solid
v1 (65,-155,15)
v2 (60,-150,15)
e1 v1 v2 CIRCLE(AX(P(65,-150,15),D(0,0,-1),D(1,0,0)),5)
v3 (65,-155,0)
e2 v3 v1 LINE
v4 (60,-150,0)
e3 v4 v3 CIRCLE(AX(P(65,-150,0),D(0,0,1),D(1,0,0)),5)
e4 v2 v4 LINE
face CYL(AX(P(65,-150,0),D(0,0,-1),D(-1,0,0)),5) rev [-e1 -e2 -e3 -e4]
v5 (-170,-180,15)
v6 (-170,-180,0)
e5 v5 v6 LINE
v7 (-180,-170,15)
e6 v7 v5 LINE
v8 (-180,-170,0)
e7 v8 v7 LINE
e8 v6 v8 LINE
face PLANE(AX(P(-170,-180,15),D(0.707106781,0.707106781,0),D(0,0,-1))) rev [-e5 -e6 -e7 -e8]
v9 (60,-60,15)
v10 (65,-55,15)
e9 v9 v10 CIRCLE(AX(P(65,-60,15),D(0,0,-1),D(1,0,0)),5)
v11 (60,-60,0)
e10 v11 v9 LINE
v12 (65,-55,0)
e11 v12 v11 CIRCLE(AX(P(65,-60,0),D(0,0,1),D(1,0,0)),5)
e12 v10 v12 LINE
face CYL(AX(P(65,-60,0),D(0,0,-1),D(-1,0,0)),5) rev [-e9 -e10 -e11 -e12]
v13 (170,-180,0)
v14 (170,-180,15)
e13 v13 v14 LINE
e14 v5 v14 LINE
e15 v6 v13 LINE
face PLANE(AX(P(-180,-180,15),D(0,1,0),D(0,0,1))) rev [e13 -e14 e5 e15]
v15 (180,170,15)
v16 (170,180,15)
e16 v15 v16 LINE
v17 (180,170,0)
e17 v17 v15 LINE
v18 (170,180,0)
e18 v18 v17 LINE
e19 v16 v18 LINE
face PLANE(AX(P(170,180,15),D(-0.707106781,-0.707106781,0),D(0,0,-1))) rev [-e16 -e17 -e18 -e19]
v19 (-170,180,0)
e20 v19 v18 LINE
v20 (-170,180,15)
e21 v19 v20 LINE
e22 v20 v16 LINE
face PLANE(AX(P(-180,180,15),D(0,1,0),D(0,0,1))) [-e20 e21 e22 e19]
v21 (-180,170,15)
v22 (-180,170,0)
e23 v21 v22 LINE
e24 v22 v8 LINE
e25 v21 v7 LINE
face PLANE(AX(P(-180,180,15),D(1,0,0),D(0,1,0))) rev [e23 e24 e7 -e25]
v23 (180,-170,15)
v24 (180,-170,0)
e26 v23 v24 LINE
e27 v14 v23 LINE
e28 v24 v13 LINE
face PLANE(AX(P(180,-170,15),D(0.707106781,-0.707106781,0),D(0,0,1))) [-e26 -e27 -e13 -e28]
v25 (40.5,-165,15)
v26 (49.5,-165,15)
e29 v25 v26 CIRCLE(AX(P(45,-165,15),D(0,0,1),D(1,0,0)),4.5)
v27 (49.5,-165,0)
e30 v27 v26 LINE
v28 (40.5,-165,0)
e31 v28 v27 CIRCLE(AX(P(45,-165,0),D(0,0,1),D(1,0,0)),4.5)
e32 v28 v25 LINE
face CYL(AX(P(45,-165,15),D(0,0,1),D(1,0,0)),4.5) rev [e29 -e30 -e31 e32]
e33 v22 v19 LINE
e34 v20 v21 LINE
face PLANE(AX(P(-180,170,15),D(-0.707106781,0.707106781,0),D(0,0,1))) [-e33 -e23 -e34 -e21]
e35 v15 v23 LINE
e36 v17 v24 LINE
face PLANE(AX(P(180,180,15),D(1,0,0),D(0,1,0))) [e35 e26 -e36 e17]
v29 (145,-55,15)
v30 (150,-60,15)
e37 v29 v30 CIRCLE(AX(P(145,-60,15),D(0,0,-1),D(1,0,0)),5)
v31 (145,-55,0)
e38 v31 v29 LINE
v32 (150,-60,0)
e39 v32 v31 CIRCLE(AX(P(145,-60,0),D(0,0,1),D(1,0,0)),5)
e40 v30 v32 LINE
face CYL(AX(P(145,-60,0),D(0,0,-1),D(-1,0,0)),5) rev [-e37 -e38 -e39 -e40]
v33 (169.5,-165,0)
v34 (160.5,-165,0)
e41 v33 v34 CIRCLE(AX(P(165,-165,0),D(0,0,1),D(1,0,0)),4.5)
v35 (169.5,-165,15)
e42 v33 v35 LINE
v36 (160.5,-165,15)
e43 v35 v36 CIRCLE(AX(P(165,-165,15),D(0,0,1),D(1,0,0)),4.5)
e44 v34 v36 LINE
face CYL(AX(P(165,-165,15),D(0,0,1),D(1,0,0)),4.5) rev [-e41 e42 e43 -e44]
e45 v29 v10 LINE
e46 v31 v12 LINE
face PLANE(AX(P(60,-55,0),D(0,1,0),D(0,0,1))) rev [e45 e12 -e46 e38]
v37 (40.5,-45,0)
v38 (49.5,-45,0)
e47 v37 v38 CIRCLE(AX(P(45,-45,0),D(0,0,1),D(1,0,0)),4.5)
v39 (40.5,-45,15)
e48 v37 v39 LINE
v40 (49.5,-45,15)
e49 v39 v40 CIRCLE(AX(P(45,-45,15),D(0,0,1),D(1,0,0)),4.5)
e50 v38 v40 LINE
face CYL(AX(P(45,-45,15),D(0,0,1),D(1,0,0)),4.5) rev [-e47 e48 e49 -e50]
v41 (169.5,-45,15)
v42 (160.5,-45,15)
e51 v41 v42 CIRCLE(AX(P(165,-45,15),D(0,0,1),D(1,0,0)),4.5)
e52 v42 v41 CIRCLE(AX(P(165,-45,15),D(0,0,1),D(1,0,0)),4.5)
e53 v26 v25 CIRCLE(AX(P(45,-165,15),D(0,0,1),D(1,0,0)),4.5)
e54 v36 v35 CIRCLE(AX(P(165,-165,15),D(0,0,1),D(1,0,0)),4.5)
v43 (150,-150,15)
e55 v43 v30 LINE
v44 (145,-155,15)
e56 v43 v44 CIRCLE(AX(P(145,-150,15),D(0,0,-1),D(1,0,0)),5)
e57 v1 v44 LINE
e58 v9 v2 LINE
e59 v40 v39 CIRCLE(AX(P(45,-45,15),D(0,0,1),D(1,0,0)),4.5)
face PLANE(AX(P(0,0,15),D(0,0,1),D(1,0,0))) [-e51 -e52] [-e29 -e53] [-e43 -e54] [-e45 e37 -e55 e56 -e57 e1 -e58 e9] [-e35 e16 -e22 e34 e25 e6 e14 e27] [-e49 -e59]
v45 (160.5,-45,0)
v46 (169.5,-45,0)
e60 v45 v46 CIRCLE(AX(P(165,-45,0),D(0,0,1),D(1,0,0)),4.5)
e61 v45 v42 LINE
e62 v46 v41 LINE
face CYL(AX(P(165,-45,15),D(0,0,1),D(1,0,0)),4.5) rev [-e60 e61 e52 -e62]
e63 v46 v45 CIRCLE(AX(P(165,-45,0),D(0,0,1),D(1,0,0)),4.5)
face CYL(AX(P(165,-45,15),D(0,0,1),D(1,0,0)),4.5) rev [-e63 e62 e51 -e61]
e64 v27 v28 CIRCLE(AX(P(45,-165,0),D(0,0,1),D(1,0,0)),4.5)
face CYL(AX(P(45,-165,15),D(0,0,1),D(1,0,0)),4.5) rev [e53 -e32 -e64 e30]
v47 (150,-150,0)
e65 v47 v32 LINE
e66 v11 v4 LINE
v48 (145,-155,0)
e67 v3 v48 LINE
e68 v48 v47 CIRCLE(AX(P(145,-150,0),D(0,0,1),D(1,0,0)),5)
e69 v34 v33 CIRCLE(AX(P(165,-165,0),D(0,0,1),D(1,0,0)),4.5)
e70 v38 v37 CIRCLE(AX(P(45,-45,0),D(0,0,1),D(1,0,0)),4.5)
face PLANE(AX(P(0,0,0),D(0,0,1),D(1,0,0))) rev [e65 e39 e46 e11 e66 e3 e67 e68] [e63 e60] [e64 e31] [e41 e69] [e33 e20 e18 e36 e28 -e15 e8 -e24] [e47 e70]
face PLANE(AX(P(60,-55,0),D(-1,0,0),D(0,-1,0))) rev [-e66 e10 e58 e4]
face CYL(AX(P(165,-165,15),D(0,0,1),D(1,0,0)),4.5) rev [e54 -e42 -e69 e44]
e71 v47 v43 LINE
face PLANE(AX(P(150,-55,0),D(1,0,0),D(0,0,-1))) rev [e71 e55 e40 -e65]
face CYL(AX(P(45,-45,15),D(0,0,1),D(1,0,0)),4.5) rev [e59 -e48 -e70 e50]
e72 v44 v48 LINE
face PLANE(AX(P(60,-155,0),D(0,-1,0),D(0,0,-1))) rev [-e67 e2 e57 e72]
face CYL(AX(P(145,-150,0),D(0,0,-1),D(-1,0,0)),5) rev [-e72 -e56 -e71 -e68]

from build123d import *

# Parameters (mm, degrees)
SKETCH1_W                    = 360
SKETCH1_H                    = 360
BOSS_EXTRUDE1_DEPTH          = 15
CHAMFER1_SIZE                = 10
F_9_0_9_DIAMETER_HOLE1_D     = 9
F_9_0_9_DIAMETER_HOLE1_DEPTH = 19.75
F_9_0_9_DIAMETER_HOLE1_TIP   = 2.703872786
SKETCH5_W                    = 90
SKETCH5_H                    = 100
CUT_EXTRUDE2_DEPTH           = 15
FILLET1_R                    = 5


with BuildPart() as part:
    # Sketch1 → Boss-Extrude1 (new body)
    with BuildSketch(Plane.XY):
        Rectangle(SKETCH1_W, SKETCH1_H)
    extrude(amount=BOSS_EXTRUDE1_DEPTH)

    # Chamfer1
    chamfer1_edges = [part.edges().sort_by_distance(p)[0] for p in [
        (-180, 180, 7.5),
        (180, 180, 7.5),
        (180, -180, 7.5),
        (-180, -180, 7.5),
    ]]
    chamfer(chamfer1_edges, length=CHAMFER1_SIZE)

    # Ø9.0 (9) Diameter Hole1
    with Locations(Plane.XY.offset(15)):
        with Locations((165, -45), (45, -45), (45, -165), (165, -165)):
            Hole(F_9_0_9_DIAMETER_HOLE1_D / 2, depth=F_9_0_9_DIAMETER_HOLE1_DEPTH)
            with Locations((0, 0, -(F_9_0_9_DIAMETER_HOLE1_DEPTH + F_9_0_9_DIAMETER_HOLE1_TIP / 2))):  # 118° drill point
                Cone(0, F_9_0_9_DIAMETER_HOLE1_D / 2, F_9_0_9_DIAMETER_HOLE1_TIP, mode=Mode.SUBTRACT)

    # Sketch5 → Cut-Extrude2 (cut)
    with BuildSketch(Plane.XY.offset(15)):
        with Locations((105, -105)):
            Rectangle(SKETCH5_W, SKETCH5_H)
    extrude(amount=-CUT_EXTRUDE2_DEPTH, mode=Mode.SUBTRACT)

    # Fillet1
    fillet1_edges = [part.edges().sort_by_distance(p)[0] for p in [
        (150, -55, 7.5),
        (150, -155, 7.5),
        (60, -155, 7.5),
        (60, -55, 7.5),
    ]]
    fillet(fillet1_edges, radius=FILLET1_R)


solid = part.part
